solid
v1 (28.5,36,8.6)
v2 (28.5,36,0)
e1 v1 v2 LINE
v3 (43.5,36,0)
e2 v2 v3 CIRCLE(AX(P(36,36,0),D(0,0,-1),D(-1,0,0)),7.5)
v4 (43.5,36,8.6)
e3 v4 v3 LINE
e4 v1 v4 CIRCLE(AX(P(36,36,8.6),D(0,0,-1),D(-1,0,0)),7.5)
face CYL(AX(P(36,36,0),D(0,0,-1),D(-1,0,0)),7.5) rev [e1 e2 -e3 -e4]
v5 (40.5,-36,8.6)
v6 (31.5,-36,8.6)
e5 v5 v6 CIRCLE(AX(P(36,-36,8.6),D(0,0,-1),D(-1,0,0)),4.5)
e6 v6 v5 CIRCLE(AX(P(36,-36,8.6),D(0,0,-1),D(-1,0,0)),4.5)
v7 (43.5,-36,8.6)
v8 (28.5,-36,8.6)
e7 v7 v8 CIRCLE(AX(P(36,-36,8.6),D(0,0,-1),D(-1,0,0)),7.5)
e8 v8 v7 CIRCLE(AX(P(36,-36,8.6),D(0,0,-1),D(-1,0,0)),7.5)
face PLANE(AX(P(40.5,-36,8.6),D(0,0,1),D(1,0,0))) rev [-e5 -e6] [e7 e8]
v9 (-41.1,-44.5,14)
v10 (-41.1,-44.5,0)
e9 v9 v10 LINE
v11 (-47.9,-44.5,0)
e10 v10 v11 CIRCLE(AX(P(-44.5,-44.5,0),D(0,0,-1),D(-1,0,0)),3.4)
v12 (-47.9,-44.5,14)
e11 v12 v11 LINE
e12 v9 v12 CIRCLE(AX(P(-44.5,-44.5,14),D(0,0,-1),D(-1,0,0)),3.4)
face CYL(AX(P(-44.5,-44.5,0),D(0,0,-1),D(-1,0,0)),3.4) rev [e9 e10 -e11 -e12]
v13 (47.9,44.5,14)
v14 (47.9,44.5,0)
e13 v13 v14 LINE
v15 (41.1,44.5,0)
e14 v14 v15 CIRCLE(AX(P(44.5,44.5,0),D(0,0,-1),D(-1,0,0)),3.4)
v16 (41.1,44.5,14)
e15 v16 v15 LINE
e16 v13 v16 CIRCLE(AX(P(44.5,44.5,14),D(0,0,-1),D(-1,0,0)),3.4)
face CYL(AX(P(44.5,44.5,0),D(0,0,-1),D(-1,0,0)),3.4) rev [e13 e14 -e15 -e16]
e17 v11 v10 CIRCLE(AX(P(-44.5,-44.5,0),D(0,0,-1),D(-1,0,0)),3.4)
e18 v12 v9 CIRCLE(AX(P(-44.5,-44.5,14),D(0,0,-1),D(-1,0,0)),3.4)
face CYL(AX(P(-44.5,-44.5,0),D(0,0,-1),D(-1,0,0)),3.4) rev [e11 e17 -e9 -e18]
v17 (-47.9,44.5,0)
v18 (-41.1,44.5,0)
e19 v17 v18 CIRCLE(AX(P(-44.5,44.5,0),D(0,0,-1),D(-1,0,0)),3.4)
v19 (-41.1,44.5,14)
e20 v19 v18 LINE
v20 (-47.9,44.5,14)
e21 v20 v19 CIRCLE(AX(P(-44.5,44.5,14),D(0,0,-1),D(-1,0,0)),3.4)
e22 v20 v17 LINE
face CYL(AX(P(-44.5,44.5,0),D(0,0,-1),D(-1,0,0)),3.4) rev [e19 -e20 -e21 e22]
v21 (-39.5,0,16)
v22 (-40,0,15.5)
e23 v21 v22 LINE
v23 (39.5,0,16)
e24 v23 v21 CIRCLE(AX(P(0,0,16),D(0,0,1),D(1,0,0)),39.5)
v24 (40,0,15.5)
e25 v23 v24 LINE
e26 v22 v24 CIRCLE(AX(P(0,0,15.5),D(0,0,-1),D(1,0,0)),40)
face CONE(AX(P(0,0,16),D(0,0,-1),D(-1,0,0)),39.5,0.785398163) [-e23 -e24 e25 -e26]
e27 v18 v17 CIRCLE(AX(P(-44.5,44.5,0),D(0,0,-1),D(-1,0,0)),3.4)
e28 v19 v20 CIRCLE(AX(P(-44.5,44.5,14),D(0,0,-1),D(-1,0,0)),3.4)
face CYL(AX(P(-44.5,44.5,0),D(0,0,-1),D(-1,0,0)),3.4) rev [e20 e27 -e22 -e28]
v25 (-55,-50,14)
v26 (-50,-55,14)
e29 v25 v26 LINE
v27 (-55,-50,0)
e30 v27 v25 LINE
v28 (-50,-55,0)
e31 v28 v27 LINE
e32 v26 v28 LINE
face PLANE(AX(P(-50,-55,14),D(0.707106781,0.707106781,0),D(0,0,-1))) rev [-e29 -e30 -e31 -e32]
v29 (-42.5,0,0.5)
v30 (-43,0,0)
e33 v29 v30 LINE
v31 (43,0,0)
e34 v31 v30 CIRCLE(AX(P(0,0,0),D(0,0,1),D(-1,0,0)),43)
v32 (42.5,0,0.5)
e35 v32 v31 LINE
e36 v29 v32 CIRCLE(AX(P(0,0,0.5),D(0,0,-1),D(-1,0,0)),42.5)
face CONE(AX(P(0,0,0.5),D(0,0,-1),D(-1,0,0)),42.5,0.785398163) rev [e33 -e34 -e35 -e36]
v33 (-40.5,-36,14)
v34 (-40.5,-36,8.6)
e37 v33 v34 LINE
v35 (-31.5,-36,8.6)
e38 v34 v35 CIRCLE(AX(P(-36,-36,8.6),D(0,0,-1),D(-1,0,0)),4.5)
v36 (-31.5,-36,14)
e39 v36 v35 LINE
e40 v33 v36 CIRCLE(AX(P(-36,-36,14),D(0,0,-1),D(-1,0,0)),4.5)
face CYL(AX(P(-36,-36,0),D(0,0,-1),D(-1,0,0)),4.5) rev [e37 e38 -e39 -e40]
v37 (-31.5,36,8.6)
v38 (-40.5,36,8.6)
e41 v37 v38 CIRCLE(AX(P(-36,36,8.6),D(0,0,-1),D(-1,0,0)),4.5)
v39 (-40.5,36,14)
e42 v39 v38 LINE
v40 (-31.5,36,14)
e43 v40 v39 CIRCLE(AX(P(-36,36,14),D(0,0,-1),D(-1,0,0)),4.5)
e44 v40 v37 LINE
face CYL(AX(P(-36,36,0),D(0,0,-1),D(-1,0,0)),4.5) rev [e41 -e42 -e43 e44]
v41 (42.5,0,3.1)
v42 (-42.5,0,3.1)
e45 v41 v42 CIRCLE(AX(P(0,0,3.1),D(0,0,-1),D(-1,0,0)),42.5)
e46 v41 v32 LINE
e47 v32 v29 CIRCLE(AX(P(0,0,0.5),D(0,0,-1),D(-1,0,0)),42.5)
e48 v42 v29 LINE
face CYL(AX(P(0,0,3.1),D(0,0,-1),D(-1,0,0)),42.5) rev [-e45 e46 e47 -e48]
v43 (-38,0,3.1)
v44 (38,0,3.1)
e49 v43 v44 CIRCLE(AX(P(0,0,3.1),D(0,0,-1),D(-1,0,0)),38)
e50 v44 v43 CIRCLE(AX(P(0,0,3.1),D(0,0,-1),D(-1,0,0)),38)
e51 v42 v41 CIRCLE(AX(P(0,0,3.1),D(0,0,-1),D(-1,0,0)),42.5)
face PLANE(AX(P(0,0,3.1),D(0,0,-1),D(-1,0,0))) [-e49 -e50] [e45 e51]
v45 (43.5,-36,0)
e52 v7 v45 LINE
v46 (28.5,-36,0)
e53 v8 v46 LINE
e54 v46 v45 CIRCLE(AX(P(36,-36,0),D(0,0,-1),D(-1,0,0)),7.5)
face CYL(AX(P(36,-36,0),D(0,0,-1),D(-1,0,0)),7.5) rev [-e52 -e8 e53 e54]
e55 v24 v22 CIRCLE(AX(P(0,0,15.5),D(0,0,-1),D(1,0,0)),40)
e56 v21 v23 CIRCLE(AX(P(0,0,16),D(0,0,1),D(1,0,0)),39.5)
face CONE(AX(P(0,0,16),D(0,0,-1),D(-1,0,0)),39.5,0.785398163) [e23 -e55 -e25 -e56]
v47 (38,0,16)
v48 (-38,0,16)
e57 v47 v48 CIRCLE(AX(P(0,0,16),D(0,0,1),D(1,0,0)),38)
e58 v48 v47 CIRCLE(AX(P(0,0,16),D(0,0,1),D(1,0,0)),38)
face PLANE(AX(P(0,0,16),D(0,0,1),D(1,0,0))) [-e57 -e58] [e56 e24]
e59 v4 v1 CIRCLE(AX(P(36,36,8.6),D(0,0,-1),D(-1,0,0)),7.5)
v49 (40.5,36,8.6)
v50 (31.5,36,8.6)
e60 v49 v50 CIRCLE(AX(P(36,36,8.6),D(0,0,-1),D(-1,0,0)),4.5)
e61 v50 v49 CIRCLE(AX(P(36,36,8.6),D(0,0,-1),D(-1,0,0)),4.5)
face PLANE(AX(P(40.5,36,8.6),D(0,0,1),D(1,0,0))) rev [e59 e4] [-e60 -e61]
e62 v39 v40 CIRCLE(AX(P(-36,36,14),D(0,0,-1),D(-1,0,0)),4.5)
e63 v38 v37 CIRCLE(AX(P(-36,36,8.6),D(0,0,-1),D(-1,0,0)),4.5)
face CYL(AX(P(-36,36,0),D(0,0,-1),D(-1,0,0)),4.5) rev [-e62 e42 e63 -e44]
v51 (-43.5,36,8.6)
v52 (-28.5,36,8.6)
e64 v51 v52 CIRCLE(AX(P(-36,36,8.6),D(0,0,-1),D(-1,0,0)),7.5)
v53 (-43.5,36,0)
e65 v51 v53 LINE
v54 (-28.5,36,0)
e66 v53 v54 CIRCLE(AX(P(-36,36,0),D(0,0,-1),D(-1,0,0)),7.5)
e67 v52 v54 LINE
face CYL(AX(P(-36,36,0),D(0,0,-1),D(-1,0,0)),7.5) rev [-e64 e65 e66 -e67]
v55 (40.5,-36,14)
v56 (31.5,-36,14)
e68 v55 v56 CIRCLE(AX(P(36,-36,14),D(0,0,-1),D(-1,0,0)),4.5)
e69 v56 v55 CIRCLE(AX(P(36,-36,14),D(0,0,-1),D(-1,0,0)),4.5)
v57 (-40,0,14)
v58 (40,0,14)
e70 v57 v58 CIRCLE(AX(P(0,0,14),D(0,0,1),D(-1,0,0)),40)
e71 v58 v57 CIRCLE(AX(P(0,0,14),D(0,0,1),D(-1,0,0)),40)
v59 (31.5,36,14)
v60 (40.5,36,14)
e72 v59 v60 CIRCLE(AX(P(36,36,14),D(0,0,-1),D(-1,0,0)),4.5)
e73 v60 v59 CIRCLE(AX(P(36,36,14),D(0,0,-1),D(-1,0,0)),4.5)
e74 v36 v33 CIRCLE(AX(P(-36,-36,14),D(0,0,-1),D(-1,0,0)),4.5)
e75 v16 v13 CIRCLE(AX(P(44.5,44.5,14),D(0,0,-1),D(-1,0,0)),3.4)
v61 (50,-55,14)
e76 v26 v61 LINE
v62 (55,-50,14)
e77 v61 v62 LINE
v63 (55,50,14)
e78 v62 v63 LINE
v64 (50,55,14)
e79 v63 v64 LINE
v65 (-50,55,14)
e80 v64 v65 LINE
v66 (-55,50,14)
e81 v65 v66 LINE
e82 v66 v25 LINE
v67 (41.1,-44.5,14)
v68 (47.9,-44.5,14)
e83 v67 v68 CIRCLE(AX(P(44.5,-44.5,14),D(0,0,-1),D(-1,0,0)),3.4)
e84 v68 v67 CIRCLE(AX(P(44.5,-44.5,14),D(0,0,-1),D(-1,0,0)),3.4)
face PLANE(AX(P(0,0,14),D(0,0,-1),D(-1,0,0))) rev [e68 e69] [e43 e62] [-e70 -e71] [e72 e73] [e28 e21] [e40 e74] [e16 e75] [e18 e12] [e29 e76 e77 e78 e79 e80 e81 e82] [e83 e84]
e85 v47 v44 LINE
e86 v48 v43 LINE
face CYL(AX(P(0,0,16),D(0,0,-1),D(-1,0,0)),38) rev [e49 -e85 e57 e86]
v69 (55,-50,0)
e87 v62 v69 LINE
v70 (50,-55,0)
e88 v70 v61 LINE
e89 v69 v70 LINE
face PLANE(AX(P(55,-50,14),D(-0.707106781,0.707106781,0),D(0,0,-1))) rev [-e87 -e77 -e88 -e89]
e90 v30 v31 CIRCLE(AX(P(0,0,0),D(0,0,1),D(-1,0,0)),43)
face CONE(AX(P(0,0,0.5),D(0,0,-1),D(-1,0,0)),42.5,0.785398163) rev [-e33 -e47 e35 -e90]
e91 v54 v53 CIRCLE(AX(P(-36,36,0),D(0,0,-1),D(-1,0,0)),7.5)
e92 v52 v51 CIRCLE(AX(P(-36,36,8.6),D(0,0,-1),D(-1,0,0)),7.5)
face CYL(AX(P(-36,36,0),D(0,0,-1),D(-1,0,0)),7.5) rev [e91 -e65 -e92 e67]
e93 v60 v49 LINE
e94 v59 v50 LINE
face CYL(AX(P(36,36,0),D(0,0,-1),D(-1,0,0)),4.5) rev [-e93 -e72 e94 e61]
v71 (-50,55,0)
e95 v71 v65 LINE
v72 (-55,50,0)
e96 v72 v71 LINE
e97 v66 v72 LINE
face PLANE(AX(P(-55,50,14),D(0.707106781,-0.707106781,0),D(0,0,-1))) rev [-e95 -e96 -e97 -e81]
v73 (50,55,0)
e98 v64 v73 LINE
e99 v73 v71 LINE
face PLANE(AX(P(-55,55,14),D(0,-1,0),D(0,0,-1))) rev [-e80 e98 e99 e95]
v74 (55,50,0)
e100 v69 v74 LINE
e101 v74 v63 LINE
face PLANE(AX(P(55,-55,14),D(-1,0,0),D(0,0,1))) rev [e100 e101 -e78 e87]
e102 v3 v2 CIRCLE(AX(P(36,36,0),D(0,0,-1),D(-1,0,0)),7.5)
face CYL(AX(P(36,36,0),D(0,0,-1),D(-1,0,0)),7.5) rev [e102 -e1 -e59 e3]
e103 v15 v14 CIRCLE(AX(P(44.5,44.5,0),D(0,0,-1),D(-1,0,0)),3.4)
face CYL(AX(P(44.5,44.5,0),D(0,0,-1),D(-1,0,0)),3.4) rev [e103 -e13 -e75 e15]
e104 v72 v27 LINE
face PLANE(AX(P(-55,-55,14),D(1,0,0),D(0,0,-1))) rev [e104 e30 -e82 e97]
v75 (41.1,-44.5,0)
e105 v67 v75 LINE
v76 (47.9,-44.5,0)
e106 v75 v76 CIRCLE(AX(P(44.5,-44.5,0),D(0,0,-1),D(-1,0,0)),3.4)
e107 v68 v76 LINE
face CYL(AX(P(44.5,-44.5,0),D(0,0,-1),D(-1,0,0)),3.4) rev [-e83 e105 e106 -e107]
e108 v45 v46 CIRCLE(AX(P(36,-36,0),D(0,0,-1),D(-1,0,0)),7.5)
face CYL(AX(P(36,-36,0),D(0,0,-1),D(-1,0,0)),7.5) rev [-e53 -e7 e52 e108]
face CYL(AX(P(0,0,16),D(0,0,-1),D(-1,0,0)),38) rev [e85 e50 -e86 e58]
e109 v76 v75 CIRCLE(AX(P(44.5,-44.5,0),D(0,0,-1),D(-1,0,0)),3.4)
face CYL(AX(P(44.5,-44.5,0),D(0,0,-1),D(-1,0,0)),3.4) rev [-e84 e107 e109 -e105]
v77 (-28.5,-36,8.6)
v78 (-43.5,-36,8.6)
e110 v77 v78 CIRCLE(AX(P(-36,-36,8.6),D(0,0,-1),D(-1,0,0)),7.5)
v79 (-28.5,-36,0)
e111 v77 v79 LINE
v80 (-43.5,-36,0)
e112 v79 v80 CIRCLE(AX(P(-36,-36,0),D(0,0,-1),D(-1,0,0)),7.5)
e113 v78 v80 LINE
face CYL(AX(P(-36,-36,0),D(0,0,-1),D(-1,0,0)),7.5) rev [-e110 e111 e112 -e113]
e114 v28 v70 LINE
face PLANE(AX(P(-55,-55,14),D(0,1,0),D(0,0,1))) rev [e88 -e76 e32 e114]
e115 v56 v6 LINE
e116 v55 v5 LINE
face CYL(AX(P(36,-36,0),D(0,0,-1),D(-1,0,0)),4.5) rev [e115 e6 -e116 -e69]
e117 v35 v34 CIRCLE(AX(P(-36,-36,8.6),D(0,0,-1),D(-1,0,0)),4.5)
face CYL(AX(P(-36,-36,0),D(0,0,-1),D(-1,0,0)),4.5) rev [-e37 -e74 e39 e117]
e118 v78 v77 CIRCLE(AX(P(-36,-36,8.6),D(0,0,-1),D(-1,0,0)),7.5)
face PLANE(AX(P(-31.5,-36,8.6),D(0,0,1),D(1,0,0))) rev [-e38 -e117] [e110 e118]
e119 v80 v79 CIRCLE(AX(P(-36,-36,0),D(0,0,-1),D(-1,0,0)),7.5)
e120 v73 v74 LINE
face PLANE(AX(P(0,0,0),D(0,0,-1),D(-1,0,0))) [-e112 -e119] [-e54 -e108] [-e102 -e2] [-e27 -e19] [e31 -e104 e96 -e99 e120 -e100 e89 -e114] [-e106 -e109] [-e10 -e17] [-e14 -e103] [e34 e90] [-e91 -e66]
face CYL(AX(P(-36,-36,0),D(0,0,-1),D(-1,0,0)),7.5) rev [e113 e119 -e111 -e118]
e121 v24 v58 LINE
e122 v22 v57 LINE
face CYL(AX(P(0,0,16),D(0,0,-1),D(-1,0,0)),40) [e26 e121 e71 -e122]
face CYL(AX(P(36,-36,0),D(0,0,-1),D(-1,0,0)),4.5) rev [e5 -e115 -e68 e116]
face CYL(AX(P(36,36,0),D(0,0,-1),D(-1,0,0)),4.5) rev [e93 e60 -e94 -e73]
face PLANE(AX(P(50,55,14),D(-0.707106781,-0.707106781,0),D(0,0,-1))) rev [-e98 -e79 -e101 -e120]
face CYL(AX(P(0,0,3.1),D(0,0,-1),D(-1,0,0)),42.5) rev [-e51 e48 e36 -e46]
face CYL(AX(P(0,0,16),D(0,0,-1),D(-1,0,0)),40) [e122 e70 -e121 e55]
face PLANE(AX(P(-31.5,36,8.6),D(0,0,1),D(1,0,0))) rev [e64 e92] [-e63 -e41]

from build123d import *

# Parameters (mm, degrees)
SKETCH_1_W                     = 110
SKETCH_1_H                     = 110
EXTRUDE_1_DEPTH                = 14
SKETCH_2_R                     = 40
SKETCH_2_R_2                   = 38
EXTRUDE_2_DEPTH                = 2
SKETCH_3_R                     = 38
CUT_EXTRUDE_1_DEPTH            = 80.031639234
SKETCH_4_R                     = 42.5
CUT_EXTRUDE_2_DEPTH            = 3.1
HOLE_WIZARD_M8_1_D             = 6.8
HOLE_WIZARD_M8_1_2_D           = 9
HOLE_WIZARD_M8_1_2_CBORE_D     = 15
HOLE_WIZARD_M8_1_2_CBORE_DEPTH = 8.6
CHAMFER_1_SIZE                 = 5
CHAMFER_2_SIZE                 = 0.5


with BuildPart() as part:
    # 草图1 → 凸台-拉伸1 (new body)
    with BuildSketch(Plane.XY):
        Rectangle(SKETCH_1_W, SKETCH_1_H)
    extrude(amount=EXTRUDE_1_DEPTH)

    # 草图2 → 凸台-拉伸2 (add)
    with BuildSketch(Plane.XY.offset(14)):
        with Locations(Location((0, 0, 0), (0, 0, 180))):
            Circle(SKETCH_2_R)
        Circle(SKETCH_2_R_2, mode=Mode.SUBTRACT)
    extrude(amount=EXTRUDE_2_DEPTH)

    # 草图3 → 切除-拉伸1 (cut, through all)
    with BuildSketch(Plane.XY.offset(14)):
        Circle(SKETCH_3_R)
    extrude(amount=-CUT_EXTRUDE_1_DEPTH, mode=Mode.SUBTRACT)

    # 草图4 → 切除-拉伸2 (cut)
    with BuildSketch(Plane(origin=(0, 0, 0), x_dir=(-1, 0, 0), z_dir=(0, 0, -1))):
        Circle(SKETCH_4_R)
    extrude(amount=-CUT_EXTRUDE_2_DEPTH, mode=Mode.SUBTRACT)

    # Hole Wizard M8 _1 (through all)
    with Locations(Plane(origin=(0, 0, 0), x_dir=(-1, 0, 0), z_dir=(0, 0, -1))):
        with Locations((-44.5, 44.5), (0, 0), (44.5, 44.5), (-44.5, -44.5), (44.5, -44.5)):
            Hole(HOLE_WIZARD_M8_1_D / 2)

    # Hole Wizard M8 _1 2 (through all)
    with Locations(Plane(origin=(0, 0, 0), x_dir=(-1, 0, 0), z_dir=(0, 0, -1))):
        with Locations((36, -36), (36, 36), (-36, -36), (-36, 36)):
            CounterBoreHole(HOLE_WIZARD_M8_1_2_D / 2, HOLE_WIZARD_M8_1_2_CBORE_D / 2, HOLE_WIZARD_M8_1_2_CBORE_DEPTH)

    # 倒角1
    chamfer_1_edges = [part.edges().sort_by_distance(p)[0] for p in [
        (55, -55, 7),
        (-55, -55, 7),
        (-55, 55, 7),
        (55, 55, 7),
    ]]
    chamfer(chamfer_1_edges, length=CHAMFER_1_SIZE)

    # 倒角2
    chamfer_2_edges = [part.edges().sort_by_distance(p)[0] for p in [
        (40, 0, 16),
        (42.5, 0, 0),
    ]]
    chamfer(chamfer_2_edges, length=CHAMFER_2_SIZE)


solid = part.part
